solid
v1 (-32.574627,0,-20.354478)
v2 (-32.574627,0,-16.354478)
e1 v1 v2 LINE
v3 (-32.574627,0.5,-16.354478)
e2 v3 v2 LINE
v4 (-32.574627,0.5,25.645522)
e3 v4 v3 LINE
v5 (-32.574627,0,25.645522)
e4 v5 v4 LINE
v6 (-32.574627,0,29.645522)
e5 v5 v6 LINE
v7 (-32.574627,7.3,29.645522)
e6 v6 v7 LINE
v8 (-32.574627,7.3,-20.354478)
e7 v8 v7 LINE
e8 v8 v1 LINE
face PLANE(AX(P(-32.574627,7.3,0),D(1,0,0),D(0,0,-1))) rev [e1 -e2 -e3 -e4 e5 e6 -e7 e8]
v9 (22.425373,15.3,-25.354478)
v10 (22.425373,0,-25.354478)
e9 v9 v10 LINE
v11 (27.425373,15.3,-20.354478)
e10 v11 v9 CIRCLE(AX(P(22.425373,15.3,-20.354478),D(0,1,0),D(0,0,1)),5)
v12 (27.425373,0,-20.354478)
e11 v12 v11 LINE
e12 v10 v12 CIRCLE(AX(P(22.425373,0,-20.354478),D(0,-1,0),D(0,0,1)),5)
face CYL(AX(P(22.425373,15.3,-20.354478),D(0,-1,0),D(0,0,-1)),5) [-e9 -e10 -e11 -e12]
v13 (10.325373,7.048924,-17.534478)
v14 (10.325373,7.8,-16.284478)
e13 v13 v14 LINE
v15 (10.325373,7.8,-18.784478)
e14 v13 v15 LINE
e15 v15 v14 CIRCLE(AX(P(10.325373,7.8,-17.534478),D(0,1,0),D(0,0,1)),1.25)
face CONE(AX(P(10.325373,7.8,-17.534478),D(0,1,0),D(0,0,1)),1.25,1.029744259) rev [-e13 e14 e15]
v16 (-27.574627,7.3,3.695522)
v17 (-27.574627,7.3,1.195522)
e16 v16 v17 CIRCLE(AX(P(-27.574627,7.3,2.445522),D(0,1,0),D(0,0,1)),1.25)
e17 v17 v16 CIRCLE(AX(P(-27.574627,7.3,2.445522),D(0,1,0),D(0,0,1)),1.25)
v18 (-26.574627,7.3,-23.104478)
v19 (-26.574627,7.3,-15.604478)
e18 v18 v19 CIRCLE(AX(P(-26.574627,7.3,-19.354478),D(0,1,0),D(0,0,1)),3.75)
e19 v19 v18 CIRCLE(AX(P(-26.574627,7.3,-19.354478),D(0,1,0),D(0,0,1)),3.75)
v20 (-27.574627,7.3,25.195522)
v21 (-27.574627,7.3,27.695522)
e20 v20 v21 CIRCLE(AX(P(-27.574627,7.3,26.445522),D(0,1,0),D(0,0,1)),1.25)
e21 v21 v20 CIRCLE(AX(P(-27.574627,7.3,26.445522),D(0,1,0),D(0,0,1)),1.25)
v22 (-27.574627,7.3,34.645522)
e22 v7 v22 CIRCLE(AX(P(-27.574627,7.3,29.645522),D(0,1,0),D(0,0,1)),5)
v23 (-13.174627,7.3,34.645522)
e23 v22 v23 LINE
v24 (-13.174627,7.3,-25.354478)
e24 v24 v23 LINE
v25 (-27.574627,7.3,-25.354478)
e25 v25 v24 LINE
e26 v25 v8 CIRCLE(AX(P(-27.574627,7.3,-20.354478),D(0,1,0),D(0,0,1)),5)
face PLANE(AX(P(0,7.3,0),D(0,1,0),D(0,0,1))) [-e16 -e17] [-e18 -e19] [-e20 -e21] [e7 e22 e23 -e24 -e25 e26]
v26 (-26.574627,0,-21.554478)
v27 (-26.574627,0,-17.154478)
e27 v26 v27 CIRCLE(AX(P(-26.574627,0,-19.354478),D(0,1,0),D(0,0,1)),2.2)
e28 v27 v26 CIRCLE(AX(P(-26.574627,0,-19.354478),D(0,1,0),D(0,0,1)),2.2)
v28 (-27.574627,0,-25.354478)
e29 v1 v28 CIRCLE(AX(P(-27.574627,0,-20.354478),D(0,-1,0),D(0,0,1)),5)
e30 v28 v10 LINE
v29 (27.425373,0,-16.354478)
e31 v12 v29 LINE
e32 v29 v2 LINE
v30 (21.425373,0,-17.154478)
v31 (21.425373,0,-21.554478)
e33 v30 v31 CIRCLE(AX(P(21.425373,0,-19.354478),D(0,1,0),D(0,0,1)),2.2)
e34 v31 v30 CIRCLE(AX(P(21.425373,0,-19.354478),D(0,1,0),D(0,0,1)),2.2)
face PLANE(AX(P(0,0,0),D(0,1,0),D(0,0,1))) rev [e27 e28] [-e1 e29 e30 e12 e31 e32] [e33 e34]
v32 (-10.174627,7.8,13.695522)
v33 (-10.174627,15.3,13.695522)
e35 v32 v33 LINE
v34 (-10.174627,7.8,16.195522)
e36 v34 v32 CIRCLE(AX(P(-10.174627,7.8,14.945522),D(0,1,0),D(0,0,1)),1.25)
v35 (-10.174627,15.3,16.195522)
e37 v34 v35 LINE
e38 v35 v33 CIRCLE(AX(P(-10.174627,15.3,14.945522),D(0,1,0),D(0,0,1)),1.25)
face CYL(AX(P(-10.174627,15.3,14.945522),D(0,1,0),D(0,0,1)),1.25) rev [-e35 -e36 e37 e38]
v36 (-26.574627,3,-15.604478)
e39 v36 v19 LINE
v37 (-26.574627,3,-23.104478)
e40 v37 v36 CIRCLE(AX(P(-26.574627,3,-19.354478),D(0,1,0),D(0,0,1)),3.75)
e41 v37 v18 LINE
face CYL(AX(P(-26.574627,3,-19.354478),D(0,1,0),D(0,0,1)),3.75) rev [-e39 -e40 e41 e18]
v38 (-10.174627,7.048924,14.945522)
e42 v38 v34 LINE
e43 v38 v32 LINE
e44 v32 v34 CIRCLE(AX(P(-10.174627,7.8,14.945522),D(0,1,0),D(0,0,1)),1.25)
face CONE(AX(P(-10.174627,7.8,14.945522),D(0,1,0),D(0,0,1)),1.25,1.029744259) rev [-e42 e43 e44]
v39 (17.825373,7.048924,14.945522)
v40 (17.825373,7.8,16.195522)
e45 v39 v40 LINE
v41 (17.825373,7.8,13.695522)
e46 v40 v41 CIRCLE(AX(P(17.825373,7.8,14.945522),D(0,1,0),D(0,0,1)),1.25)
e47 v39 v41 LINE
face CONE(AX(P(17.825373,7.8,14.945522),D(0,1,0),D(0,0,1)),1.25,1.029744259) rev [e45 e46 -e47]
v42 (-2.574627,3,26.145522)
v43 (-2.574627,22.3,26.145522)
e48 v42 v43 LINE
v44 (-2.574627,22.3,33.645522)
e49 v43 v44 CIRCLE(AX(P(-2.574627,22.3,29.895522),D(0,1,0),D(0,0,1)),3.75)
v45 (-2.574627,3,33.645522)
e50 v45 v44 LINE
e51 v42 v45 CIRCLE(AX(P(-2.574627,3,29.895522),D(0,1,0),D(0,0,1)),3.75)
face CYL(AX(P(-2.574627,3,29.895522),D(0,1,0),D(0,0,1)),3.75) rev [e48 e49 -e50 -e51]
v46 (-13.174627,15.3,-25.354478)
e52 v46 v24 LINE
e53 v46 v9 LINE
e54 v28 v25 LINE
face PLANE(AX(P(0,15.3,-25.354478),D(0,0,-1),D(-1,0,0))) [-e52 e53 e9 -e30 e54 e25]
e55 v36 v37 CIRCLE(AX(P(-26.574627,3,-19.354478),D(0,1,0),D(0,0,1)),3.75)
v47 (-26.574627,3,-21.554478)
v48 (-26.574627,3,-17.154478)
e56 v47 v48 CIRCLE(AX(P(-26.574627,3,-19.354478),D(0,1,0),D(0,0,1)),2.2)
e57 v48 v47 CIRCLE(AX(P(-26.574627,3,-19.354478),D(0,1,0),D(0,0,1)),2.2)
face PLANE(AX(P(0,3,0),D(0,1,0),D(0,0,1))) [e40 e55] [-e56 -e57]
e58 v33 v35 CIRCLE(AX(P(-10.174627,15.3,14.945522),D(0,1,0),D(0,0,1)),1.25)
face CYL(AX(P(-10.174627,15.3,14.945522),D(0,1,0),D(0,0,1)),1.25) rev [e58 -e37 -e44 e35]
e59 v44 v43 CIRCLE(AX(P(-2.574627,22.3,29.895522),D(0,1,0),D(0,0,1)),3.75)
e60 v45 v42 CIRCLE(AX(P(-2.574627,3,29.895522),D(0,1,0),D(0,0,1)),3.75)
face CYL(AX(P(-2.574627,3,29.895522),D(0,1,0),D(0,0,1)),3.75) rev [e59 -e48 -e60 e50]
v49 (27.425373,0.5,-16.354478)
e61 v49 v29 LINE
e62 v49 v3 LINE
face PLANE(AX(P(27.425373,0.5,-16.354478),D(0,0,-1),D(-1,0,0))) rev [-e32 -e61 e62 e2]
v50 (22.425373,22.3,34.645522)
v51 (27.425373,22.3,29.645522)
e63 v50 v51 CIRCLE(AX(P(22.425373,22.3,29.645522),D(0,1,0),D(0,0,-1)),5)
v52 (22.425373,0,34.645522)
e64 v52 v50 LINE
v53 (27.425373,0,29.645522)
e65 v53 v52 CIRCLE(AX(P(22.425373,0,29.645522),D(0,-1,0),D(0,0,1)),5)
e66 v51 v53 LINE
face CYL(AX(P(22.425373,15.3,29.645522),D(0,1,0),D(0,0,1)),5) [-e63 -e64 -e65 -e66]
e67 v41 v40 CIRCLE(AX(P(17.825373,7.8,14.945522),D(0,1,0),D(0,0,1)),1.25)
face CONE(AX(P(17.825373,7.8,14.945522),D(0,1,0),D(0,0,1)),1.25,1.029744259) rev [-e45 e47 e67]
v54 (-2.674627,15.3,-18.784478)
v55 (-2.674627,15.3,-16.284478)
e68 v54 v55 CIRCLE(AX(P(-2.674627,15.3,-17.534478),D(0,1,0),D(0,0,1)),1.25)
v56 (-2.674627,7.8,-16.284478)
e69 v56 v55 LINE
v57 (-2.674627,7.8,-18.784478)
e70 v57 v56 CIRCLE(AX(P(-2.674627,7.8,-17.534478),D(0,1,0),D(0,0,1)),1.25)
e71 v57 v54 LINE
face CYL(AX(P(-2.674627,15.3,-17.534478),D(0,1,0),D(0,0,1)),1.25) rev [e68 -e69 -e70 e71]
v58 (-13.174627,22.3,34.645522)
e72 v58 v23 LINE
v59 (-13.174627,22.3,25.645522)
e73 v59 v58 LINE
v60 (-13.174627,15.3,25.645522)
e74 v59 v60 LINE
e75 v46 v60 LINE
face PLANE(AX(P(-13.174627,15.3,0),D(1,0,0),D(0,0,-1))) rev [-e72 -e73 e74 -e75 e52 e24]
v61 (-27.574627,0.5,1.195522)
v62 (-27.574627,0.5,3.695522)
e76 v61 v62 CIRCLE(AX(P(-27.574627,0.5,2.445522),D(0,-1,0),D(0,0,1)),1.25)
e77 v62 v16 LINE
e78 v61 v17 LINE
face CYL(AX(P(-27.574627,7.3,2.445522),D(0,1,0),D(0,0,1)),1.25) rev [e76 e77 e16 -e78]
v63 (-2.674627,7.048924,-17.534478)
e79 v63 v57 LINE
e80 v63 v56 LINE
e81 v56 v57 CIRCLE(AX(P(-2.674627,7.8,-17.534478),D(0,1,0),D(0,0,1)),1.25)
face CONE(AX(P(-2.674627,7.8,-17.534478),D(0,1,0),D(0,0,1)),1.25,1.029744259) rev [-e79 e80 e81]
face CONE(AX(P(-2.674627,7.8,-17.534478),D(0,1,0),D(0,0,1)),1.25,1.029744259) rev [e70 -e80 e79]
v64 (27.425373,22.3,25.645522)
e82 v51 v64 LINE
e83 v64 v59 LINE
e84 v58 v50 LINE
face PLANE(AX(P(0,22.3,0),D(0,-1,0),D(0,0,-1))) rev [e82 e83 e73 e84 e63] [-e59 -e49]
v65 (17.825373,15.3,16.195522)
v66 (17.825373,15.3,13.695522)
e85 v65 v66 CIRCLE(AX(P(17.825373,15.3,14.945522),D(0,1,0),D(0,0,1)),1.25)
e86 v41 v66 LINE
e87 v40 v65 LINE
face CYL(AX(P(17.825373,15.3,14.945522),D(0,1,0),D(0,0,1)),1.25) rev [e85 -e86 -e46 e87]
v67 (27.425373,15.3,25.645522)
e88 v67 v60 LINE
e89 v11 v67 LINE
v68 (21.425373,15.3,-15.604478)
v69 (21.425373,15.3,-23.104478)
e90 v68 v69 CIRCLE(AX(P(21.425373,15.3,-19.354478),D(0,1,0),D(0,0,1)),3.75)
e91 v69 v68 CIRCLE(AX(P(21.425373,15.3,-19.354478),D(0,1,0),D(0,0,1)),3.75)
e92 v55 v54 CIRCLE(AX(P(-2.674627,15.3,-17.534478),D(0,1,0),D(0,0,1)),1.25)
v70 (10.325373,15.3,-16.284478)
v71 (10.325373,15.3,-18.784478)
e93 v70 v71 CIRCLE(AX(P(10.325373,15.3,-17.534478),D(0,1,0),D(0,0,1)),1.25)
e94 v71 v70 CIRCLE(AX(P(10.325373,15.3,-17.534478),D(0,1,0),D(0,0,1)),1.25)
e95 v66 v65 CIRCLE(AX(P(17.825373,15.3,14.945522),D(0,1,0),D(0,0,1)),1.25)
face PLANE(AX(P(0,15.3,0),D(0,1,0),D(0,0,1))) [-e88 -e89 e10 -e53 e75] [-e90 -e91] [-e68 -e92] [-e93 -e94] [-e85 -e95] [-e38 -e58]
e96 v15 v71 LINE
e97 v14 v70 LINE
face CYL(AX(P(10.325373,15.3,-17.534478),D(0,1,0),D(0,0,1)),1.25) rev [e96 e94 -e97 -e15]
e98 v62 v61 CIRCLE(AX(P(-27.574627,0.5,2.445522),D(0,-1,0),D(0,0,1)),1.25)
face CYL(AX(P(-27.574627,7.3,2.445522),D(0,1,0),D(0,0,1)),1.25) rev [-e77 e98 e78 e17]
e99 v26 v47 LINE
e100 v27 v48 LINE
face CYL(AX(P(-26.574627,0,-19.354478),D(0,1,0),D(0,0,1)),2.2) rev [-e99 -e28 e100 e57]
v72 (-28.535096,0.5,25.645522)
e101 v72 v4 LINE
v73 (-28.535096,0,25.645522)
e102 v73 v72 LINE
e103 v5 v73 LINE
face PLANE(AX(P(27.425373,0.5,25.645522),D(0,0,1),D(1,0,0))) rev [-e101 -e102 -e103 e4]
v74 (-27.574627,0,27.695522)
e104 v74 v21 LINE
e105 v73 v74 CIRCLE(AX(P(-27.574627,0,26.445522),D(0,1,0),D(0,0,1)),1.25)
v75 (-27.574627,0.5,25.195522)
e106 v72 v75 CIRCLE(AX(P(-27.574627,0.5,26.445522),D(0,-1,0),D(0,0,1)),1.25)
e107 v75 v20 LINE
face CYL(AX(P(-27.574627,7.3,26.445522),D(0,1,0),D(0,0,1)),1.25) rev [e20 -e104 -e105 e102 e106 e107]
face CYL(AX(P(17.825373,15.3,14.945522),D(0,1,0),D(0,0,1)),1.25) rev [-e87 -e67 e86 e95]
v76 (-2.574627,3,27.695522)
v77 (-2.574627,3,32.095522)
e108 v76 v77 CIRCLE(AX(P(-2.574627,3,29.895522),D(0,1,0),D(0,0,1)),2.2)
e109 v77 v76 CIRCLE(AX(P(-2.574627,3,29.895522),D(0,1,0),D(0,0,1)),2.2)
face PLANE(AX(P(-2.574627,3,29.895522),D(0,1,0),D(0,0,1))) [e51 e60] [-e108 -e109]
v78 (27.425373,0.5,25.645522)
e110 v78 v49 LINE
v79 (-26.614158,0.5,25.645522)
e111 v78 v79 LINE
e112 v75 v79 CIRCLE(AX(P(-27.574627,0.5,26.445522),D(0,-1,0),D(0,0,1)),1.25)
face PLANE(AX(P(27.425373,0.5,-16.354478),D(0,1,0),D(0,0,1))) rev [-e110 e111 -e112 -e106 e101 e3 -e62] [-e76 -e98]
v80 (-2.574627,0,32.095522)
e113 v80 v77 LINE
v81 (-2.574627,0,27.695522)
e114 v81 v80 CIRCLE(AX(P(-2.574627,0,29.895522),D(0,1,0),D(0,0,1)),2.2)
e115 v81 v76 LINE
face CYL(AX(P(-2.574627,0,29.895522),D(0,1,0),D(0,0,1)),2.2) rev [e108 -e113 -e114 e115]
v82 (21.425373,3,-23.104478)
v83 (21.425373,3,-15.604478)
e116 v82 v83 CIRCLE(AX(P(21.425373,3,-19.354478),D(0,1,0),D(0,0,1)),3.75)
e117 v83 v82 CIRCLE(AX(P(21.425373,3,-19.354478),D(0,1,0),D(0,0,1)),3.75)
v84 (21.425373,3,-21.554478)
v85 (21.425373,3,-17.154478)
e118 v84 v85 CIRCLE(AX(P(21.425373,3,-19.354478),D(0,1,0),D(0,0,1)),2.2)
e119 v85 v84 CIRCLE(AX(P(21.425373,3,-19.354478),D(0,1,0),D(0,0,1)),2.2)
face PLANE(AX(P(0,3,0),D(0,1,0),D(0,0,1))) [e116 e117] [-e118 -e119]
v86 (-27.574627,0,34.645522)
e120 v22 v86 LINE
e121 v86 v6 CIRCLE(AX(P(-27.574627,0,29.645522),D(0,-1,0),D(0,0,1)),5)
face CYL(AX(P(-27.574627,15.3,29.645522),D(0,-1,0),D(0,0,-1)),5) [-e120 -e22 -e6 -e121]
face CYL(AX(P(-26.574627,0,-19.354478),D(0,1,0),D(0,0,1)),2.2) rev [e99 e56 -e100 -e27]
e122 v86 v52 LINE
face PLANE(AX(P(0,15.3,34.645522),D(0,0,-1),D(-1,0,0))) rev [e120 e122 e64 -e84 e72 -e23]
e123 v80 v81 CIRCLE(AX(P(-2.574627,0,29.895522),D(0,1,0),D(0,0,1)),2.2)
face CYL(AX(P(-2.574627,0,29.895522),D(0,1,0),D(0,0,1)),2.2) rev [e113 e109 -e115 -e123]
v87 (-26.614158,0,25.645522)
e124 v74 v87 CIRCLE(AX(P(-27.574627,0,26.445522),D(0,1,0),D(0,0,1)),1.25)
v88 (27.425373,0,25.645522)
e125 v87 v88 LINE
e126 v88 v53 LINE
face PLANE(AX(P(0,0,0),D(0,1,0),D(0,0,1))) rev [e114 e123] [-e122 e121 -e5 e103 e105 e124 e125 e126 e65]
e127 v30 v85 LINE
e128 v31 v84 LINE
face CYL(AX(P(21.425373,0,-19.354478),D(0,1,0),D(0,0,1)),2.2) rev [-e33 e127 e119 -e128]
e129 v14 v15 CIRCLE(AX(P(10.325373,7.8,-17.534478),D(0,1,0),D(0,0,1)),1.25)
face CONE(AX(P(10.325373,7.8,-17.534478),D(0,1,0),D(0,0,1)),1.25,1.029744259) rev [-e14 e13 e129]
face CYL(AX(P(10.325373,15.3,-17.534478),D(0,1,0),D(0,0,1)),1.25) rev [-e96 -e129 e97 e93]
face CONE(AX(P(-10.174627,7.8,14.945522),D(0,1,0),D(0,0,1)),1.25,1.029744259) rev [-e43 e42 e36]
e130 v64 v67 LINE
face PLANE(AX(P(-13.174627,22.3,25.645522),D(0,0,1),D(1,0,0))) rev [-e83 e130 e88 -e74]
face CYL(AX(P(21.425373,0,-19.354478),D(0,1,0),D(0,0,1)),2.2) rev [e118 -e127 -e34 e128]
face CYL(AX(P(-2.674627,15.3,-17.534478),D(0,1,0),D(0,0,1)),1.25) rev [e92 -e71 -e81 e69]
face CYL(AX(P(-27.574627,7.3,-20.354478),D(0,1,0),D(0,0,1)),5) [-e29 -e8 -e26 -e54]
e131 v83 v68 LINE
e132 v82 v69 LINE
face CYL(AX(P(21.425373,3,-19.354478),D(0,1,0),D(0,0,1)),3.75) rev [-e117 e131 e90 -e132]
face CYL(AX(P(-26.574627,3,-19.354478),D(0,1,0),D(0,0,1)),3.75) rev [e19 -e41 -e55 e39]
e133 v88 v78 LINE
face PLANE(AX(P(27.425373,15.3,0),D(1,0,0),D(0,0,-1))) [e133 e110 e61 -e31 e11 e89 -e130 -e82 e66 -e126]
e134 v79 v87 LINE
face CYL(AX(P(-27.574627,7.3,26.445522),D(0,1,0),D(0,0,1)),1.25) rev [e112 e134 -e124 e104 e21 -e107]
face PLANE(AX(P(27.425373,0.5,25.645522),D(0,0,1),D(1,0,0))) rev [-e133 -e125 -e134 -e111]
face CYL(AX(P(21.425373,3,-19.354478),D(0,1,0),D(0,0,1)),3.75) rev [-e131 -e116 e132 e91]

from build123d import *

# Parameters (mm, degrees)
SKETCH_1_3_W          = 40.6
SKETCH_1_3_H          = 60
BOSS_EXTRUDE1_DEPTH   = 15.3
SKETCH_1_3_2_W        = 19.4
SKETCH_1_3_2_H        = 60
BOSS_EXTRUDE2_DEPTH   = 7.3
SKETCH2_W             = 40.6
SKETCH2_H             = 9
BOSS_EXTRUDE3_DEPTH   = 7
M3_TAPPED_HOLE1_D     = 2.5
M3_TAPPED_HOLE1_DEPTH = 7.5
M3_TAPPED_HOLE1_TIP   = 0.751075774
M3_TAPPED_HOLE2_D     = 2.5
M3_TAPPED_HOLE2_DEPTH = 7.5
M3_TAPPED_HOLE2_TIP   = 0.751075774
FILLET1_R             = 5
SKETCH11_W            = 42
SKETCH11_H            = 4.723838164
CUT_EXTRUDE5_DEPTH    = 73.78462902
SKETCH12_R            = 3.75
CUT_EXTRUDE6_DEPTH    = 19.3
SKETCH13_R            = 2.2
CUT_EXTRUDE7_DEPTH    = 52.321618612


with BuildPart() as part:
    # Sketch 1_3 → Boss-Extrude1 (new body)
    with BuildSketch(Plane(origin=(0, 0, 0), x_dir=(1, 0, 0), z_dir=(0, 1, 0))):
        with Locations((7.125373134, -4.645522388)):
            Rectangle(SKETCH_1_3_W, SKETCH_1_3_H)
    extrude(amount=BOSS_EXTRUDE1_DEPTH)

    # Sketch 1_3 2 → Boss-Extrude2 (add)
    with BuildSketch(Plane(origin=(0, 0, 0), x_dir=(1, 0, 0), z_dir=(0, 1, 0))):
        with Locations((-22.874626866, -4.645522388)):
            Rectangle(SKETCH_1_3_2_W, SKETCH_1_3_2_H)
    extrude(amount=BOSS_EXTRUDE2_DEPTH)

    # Sketch2 → Boss-Extrude3 (add)
    with BuildSketch(Plane(origin=(0, 15.3, 0), x_dir=(1, 0, 0), z_dir=(0, 1, 0))):
        with Locations((7.125373134, -30.145522388)):
            Rectangle(SKETCH2_W, SKETCH2_H)
    extrude(amount=BOSS_EXTRUDE3_DEPTH)

    # M3 Tapped Hole1
    with Locations(Plane(origin=(0, 7.3, 0), x_dir=(1, 0, 0), z_dir=(0, 1, 0))):
        with Locations((-27.574626866, -2.445522388), (-27.574626866, -26.445522388)):
            Hole(M3_TAPPED_HOLE1_D / 2, depth=M3_TAPPED_HOLE1_DEPTH)
            with Locations((0, 0, -(M3_TAPPED_HOLE1_DEPTH + M3_TAPPED_HOLE1_TIP / 2))):  # 118° drill point
                Cone(0, M3_TAPPED_HOLE1_D / 2, M3_TAPPED_HOLE1_TIP, mode=Mode.SUBTRACT)

    # M3 Tapped Hole2
    with Locations(Plane(origin=(0, 15.3, 0), x_dir=(1, 0, 0), z_dir=(0, 1, 0))):
        with Locations((-10.174626866, -14.945522388), (17.825373134, -14.945522388), (-2.674626866, 17.534477612), (10.325373134, 17.534477612)):
            Hole(M3_TAPPED_HOLE2_D / 2, depth=M3_TAPPED_HOLE2_DEPTH)
            with Locations((0, 0, -(M3_TAPPED_HOLE2_DEPTH + M3_TAPPED_HOLE2_TIP / 2))):  # 118° drill point
                Cone(0, M3_TAPPED_HOLE2_D / 2, M3_TAPPED_HOLE2_TIP, mode=Mode.SUBTRACT)

    # Fillet1
    fillet1_edges = [part.edges().sort_by_distance(p)[0] for p in [
        (-32.574626866, 3.65, -25.354477612),
        (-32.574626866, 3.65, 34.645522388),
        (27.425373134, 11.15, 34.645522388),
        (27.425373134, 7.65, -25.354477612),
    ]]
    fillet(fillet1_edges, radius=FILLET1_R)

    # Sketch11 → Cut-Extrude5 (cut, through all)
    with BuildSketch(Plane.ZY.offset(32.574626866)):
        with Locations((4.645522388, -1.861919082)):
            Rectangle(SKETCH11_W, SKETCH11_H)
    extrude(amount=-CUT_EXTRUDE5_DEPTH, mode=Mode.SUBTRACT)

    # Sketch12 → Cut-Extrude6 (cut)
    with BuildSketch(Plane(origin=(0, 22.3, 0), x_dir=(1, 0, 0), z_dir=(0, 1, 0))):
        with Locations(Location((21.425373134, 19.354477612, 0), (0, 0, 270))):
            Circle(SKETCH12_R)
        with Locations(Location((-26.574626866, 19.354477612, 0), (0, 0, 270))):
            Circle(SKETCH12_R)
        with Locations(Location((-2.574626866, -29.895522388, 0), (0, 0, 270))):
            Circle(SKETCH12_R)
    extrude(amount=-CUT_EXTRUDE6_DEPTH, mode=Mode.SUBTRACT)

    # Sketch13 → Cut-Extrude7 (cut, through all)
    with BuildSketch(Plane(origin=(0, 3, 0), x_dir=(1, 0, 0), z_dir=(0, 1, 0))):
        with Locations(Location((-2.574626866, -29.895522388, 0), (0, 0, 270))):
            Circle(SKETCH13_R)
        with Locations(Location((21.425373134, 19.354477612, 0), (0, 0, 270))):
            Circle(SKETCH13_R)
        with Locations(Location((-26.574626866, 19.354477612, 0), (0, 0, 270))):
            Circle(SKETCH13_R)
    extrude(amount=-CUT_EXTRUDE7_DEPTH, mode=Mode.SUBTRACT)


solid = part.part
